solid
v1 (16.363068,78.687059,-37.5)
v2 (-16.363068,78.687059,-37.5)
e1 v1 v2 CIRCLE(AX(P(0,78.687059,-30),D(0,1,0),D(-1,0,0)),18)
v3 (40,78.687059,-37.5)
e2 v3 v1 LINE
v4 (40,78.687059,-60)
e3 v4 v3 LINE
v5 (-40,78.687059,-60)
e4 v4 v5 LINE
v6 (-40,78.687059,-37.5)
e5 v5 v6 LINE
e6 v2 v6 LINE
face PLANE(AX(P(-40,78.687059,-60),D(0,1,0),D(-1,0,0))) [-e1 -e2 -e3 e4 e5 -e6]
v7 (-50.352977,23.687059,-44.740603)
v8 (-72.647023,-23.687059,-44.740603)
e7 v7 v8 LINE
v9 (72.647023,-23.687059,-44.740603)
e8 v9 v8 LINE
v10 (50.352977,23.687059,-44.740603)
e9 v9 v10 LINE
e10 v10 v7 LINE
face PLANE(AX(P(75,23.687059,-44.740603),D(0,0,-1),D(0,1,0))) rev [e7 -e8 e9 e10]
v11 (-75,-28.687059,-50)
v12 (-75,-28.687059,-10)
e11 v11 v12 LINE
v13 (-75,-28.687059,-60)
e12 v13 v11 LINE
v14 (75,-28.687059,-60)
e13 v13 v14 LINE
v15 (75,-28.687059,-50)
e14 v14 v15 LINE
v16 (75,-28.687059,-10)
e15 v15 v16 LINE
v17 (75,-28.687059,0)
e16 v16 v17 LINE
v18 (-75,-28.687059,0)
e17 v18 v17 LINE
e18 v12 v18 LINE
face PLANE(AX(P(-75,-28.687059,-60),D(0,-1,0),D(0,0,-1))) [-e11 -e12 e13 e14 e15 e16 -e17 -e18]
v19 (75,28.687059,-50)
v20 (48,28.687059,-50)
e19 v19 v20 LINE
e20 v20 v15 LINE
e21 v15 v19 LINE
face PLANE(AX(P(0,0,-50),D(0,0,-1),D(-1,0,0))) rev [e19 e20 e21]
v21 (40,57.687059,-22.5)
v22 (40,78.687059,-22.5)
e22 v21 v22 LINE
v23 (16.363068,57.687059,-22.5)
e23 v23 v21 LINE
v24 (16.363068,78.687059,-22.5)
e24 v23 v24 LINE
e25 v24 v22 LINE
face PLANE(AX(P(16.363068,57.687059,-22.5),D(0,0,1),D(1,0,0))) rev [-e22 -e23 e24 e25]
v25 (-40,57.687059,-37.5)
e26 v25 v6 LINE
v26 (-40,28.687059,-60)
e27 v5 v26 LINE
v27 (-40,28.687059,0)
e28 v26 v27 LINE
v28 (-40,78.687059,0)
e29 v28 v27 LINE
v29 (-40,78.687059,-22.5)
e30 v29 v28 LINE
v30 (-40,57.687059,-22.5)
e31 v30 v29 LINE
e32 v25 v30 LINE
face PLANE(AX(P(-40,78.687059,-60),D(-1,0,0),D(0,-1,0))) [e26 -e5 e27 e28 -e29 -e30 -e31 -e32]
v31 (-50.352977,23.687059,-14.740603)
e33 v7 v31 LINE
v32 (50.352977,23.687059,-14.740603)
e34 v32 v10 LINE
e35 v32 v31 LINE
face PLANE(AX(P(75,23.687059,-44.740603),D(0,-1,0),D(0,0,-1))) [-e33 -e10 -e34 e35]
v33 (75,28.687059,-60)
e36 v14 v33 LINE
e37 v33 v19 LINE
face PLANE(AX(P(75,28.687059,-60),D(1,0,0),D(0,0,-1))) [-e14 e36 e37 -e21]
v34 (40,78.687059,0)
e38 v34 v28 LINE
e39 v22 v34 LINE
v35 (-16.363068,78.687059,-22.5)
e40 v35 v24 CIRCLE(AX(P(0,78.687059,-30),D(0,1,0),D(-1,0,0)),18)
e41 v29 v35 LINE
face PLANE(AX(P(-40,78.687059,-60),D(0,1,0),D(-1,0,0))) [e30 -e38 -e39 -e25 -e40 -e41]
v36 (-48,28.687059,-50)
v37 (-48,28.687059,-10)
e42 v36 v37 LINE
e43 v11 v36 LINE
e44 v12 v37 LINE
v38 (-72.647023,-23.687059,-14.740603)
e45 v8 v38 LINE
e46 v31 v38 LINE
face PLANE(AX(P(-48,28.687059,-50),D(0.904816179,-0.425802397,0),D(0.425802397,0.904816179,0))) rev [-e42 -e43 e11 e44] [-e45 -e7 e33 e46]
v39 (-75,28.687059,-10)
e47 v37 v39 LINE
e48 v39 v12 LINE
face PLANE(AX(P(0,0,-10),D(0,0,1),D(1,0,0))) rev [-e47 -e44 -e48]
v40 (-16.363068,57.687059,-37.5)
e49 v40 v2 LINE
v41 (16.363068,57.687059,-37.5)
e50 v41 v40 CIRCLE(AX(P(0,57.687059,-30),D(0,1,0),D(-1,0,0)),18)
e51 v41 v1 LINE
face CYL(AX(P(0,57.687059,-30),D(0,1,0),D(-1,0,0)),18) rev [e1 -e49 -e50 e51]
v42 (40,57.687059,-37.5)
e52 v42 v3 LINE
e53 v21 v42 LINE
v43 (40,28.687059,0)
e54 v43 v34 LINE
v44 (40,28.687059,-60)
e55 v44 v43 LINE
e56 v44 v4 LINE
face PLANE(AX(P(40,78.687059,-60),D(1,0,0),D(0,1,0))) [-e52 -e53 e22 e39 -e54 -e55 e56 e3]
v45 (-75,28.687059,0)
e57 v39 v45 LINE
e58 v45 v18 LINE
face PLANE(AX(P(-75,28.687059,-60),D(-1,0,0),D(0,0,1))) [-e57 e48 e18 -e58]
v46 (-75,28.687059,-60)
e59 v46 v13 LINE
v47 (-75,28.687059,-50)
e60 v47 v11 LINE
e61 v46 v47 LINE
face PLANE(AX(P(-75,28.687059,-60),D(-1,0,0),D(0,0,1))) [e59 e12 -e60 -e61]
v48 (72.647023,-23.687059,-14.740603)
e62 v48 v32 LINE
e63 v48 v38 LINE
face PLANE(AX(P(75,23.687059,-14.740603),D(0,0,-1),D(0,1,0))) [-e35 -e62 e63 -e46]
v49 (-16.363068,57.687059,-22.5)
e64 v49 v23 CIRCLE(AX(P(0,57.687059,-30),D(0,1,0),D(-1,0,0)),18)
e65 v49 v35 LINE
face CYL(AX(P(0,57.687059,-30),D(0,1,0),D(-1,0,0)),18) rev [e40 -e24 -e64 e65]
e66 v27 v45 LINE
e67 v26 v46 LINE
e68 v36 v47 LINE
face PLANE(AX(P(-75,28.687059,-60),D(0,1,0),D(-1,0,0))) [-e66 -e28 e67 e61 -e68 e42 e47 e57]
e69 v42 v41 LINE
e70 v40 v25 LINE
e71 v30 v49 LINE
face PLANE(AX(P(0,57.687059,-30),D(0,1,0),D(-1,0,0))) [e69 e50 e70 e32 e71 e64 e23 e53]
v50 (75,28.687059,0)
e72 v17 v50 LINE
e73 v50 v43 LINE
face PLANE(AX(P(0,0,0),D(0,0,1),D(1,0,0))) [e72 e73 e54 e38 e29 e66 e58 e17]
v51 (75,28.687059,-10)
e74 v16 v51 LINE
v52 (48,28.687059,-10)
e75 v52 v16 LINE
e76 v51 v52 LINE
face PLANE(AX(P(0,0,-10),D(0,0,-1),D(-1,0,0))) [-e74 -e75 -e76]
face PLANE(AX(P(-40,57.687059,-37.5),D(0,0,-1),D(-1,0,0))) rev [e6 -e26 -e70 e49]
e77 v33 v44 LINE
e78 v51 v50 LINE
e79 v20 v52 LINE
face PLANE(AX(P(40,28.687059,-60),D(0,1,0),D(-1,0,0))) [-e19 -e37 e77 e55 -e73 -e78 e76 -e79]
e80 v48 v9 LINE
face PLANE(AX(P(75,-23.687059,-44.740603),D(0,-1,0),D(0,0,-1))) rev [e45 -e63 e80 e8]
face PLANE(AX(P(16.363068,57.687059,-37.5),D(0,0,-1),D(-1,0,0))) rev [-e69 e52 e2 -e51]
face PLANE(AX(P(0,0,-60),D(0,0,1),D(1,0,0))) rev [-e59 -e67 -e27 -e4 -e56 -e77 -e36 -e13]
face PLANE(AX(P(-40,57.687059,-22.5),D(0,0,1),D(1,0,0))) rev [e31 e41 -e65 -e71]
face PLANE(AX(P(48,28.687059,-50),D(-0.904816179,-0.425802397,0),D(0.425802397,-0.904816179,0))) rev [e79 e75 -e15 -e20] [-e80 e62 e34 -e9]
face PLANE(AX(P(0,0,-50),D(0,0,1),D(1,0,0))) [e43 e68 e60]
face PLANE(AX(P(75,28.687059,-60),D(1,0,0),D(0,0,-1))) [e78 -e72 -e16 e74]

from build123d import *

# Parameters (mm, degrees)
BASE_BLOCK_DEPTH              = 60
TOP_SLOT_WITH_BORE_SEAT_DEPTH = 21
END_CHANNEL_PROFILE_W         = 30
END_CHANNEL_PROFILE_H         = 47.374117648
END_CHANNEL_CUT_DEPTH         = 180.69878471
TRIANGULAR_POCKET_CUT_DEPTH   = 40


with BuildPart() as part:
    # Base Block Profile → Base Block (new body)
    with BuildSketch(Plane.XY):
        Polygon((40, 28.687058824), (75, 28.687058824), (75, -28.687058824), (-75, -28.687058824), (-75, 28.687058824), (-40, 28.687058824), (-40, 78.687058824), (40, 78.687058824), align=None)
    extrude(amount=-BASE_BLOCK_DEPTH)

    # Top Slot Profile → Top Slot With Bore Seat (cut)
    with BuildSketch(Plane(origin=(0, 78.687058824, 0), x_dir=(1, 0, 0), z_dir=(0, 1, 0))):
        with BuildLine():
            Line((-40, 37.5), (-16.363068172, 37.5))
            ThreePointArc((-16.363068172, 37.5), (0, 48), (16.363068172, 37.5))
            Line((16.363068172, 37.5), (40, 37.5))
            Line((40, 37.5), (40, 22.5))
            Line((40, 22.5), (16.363068172, 22.5))
            ThreePointArc((16.363068172, 22.5), (0, 12), (-16.363068172, 22.5))
            Line((-16.363068172, 22.5), (-40, 22.5))
            Line((-40, 22.5), (-40, 37.5))
        make_face()
    extrude(amount=-TOP_SLOT_WITH_BORE_SEAT_DEPTH, mode=Mode.SUBTRACT)

    # End Channel Profile → End Channel Cut (cut, through all)
    with BuildSketch(Plane.ZY.offset(75)):
        with Locations((-29.740602956, 0)):
            Rectangle(END_CHANNEL_PROFILE_W, END_CHANNEL_PROFILE_H)
    extrude(amount=-END_CHANNEL_CUT_DEPTH, mode=Mode.SUBTRACT)

    # Triangular Pocket Profile → Triangular Pocket Cut (cut)
    with BuildSketch(Plane.XY.offset(-10)):
        Polygon((-48, 28.687058824), (-75, -28.687058824), (-75, 28.687058824), align=None)
        Polygon((48, 28.687058824), (75, -28.687058824), (75, 28.687058824), align=None)
    extrude(amount=-TRIANGULAR_POCKET_CUT_DEPTH, mode=Mode.SUBTRACT)


solid = part.part
